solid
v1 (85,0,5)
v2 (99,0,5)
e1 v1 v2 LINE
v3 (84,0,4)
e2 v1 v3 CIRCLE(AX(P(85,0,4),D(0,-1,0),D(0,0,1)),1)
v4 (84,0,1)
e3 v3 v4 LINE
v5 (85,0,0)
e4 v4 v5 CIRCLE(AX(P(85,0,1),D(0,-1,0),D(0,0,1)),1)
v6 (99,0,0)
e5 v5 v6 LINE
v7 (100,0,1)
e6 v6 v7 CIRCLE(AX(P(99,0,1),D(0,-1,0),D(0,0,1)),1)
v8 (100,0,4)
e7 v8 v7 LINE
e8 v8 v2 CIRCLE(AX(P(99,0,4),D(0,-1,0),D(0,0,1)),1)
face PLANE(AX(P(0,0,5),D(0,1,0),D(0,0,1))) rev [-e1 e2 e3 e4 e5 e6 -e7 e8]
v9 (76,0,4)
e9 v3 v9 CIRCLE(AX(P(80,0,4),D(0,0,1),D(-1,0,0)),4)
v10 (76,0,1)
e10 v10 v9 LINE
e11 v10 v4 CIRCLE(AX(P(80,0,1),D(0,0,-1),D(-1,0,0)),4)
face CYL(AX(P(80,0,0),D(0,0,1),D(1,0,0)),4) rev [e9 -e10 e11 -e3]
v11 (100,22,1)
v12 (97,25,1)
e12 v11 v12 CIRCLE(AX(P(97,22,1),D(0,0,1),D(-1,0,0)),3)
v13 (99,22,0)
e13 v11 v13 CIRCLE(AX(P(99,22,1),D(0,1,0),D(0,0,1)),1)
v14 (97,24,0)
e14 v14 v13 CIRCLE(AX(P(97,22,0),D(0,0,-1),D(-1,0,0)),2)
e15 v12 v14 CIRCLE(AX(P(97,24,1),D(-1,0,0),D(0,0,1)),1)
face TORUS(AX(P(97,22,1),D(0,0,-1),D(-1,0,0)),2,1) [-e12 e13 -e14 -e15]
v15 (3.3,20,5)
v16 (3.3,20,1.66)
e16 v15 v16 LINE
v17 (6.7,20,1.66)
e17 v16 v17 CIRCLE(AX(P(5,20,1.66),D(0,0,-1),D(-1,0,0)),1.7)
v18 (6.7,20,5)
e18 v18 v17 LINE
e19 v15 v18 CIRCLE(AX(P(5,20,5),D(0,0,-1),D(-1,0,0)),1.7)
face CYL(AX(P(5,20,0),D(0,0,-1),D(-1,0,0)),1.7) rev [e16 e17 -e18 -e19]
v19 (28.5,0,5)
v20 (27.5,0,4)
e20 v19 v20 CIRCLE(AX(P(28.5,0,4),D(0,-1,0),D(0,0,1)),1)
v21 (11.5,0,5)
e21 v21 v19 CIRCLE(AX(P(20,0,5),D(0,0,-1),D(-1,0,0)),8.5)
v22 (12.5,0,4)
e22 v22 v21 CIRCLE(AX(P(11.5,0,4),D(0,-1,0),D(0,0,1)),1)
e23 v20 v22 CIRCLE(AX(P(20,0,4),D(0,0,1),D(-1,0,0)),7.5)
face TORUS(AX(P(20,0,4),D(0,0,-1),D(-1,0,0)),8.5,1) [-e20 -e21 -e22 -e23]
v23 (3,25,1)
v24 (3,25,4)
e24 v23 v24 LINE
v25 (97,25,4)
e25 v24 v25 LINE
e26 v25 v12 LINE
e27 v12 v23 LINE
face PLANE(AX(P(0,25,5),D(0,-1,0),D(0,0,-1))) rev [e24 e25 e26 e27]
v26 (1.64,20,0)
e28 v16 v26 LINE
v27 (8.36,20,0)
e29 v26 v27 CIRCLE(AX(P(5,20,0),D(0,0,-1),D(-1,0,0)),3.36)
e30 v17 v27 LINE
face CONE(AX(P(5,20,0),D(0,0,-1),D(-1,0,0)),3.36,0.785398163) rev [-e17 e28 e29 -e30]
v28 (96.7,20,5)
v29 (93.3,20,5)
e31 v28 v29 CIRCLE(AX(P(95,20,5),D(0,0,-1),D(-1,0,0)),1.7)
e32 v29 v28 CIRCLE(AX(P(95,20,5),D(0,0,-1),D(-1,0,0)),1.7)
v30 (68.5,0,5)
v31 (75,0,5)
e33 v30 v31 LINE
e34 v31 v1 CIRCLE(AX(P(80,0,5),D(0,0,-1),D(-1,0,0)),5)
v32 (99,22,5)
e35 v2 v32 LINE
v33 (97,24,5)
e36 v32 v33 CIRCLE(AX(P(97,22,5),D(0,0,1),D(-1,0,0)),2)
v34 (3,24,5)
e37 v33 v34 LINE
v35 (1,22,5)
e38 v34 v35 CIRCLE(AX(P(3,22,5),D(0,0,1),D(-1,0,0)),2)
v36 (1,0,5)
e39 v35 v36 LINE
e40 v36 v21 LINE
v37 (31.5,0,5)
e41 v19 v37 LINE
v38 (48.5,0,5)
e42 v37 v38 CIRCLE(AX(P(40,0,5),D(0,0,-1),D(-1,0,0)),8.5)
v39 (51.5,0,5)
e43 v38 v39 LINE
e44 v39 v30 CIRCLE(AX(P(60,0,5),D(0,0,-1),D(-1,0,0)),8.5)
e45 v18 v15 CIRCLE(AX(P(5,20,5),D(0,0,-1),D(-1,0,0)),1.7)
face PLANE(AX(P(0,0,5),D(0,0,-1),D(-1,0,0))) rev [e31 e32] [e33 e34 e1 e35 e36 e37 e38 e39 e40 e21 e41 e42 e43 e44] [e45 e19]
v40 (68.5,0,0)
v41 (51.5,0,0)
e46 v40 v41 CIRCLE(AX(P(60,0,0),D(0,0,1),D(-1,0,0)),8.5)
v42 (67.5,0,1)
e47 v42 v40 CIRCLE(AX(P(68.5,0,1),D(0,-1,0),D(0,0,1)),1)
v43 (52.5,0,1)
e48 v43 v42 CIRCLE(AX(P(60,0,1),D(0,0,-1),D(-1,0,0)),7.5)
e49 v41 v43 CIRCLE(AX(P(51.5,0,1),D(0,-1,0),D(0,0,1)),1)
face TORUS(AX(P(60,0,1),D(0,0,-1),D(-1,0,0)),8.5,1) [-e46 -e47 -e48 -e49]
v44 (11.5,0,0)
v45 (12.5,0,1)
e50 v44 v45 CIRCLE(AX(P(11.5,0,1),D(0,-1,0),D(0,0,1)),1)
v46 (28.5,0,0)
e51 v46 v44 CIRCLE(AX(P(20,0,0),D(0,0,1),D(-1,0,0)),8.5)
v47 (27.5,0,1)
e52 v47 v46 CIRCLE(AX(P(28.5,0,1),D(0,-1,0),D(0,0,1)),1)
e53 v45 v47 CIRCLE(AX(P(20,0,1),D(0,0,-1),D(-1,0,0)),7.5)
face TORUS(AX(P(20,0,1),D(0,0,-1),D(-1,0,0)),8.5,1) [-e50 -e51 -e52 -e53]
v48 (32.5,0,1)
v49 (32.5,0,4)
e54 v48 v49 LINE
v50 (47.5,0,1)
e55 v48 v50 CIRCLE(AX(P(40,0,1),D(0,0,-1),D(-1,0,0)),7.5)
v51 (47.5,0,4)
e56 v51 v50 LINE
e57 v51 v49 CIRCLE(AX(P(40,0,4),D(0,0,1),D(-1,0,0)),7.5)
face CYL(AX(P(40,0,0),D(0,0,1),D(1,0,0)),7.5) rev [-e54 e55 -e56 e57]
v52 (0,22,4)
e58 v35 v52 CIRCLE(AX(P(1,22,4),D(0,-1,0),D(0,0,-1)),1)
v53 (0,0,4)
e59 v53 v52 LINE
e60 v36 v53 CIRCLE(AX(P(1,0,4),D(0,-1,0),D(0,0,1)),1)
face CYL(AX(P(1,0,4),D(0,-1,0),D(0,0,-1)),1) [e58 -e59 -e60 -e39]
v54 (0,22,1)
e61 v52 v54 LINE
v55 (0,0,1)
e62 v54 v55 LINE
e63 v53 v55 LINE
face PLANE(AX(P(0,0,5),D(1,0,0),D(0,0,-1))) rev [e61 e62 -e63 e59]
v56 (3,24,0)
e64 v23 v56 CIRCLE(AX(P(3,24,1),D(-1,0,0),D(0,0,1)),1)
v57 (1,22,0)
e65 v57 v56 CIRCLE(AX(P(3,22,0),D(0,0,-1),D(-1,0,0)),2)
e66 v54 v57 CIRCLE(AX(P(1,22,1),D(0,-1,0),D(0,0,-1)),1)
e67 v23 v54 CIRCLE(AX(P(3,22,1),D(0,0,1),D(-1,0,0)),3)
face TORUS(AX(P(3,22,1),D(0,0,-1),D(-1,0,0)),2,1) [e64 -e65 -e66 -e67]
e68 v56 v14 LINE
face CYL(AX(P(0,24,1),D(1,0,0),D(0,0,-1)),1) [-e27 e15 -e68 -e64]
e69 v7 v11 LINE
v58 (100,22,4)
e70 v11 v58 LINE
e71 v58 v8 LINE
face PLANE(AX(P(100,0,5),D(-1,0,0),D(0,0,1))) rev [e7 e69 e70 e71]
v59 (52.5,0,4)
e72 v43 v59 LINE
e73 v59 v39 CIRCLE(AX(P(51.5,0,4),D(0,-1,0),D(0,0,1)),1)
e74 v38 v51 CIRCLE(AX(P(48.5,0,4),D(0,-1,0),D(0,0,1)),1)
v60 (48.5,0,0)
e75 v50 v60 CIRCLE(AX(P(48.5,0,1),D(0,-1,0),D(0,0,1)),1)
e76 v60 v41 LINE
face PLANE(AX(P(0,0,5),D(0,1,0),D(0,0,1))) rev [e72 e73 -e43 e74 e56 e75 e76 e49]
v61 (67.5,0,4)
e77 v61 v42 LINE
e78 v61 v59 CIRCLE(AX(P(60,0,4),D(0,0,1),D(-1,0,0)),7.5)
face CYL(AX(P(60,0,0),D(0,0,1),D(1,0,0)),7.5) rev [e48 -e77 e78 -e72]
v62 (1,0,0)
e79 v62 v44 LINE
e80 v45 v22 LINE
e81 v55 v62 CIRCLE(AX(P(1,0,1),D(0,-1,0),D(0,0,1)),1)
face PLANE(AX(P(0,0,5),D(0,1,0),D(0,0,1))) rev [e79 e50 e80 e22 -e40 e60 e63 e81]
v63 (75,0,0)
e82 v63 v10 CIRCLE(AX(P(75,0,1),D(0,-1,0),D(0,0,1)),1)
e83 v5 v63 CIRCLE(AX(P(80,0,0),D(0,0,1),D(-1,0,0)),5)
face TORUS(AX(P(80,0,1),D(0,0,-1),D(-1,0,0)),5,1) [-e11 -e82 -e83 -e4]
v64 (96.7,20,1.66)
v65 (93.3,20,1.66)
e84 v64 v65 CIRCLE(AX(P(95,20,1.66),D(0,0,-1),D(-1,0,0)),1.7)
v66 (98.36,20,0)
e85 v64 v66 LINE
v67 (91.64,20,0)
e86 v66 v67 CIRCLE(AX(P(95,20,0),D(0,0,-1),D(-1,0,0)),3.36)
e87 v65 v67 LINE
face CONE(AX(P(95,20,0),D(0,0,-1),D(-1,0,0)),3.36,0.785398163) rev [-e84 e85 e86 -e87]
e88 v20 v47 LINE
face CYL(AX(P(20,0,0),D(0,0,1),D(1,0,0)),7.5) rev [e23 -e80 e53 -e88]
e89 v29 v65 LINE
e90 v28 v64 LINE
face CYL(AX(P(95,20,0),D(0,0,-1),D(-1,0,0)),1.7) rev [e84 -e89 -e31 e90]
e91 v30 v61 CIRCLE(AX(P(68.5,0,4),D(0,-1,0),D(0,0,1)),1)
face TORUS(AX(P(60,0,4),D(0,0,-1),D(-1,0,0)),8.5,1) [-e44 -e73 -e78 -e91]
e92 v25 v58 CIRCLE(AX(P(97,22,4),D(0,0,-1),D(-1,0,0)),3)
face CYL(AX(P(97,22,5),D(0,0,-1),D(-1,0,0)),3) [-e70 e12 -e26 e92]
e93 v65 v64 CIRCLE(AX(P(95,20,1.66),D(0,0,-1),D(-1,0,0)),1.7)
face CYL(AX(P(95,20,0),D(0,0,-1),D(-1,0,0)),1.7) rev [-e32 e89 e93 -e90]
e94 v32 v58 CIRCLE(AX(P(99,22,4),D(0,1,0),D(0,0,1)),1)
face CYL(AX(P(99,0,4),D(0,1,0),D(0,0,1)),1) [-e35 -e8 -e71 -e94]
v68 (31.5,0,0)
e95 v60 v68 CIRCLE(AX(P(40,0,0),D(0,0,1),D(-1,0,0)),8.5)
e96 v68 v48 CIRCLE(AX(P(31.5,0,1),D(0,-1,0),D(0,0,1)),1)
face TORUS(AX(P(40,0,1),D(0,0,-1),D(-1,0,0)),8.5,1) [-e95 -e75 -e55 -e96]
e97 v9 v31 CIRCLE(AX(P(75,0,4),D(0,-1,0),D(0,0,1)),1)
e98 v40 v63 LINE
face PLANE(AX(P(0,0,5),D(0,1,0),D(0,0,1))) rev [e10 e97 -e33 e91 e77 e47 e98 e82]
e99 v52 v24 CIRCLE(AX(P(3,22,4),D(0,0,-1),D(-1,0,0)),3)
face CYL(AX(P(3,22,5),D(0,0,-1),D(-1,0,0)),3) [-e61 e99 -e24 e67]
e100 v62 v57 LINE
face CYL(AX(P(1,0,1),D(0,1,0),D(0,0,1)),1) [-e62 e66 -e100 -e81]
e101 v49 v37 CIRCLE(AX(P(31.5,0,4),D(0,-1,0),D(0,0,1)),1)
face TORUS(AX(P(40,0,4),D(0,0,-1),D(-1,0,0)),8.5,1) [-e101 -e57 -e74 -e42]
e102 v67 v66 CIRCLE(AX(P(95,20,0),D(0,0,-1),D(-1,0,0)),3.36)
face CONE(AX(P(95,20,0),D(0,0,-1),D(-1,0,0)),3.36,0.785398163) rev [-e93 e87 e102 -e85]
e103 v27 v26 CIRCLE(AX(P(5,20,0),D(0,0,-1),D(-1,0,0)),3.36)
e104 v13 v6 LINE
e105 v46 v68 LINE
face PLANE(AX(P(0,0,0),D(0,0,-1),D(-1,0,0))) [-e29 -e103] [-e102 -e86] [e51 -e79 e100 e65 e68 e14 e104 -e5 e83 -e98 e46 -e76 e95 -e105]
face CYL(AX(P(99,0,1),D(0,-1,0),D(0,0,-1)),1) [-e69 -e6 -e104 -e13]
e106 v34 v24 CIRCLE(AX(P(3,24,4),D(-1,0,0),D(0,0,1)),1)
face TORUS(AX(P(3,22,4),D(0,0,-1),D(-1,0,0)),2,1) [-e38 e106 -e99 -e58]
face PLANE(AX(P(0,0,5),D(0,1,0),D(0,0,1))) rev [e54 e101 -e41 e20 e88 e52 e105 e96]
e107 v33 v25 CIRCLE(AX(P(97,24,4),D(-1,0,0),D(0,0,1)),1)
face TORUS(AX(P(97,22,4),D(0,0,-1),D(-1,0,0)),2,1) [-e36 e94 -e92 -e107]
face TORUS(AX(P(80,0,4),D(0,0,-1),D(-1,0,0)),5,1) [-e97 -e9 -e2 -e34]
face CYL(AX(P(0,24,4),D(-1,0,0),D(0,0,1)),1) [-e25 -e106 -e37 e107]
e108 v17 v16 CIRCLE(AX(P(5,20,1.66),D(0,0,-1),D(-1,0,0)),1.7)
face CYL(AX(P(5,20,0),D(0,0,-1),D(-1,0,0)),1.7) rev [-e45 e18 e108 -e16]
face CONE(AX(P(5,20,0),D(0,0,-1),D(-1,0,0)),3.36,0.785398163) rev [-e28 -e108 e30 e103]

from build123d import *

# Parameters (mm, degrees)
SKETCH_1_W                   = 100
SKETCH_1_H                   = 25
EXTRUDE_1_DEPTH              = 5
SKETCH_2_R                   = 7.5
SKETCH_2_R_2                 = 4
CUT_EXTRUDE_1_DEPTH          = 104.198837203
HOLE_WIZARD_M3_1_D           = 3.4
HOLE_WIZARD_M3_1_CSINK_D     = 6.72
HOLE_WIZARD_M3_1_CSINK_ANGLE = 90
FILLET_1_R                   = 3
FILLET_2_R                   = 1


with BuildPart() as part:
    # 草图1 → 凸台-拉伸1 (new body)
    with BuildSketch(Plane.XY):
        with Locations((50, 12.5)):
            Rectangle(SKETCH_1_W, SKETCH_1_H)
    extrude(amount=EXTRUDE_1_DEPTH)

    # 草图2 → 切除-拉伸1 (cut, through all)
    with BuildSketch(Plane.XY.offset(5)):
        with Locations((20, 0)):
            Circle(SKETCH_2_R)
        with Locations((40, 0)):
            Circle(SKETCH_2_R)
        with Locations((60, 0)):
            Circle(SKETCH_2_R)
        with Locations((80, 0)):
            Circle(SKETCH_2_R_2)
    extrude(amount=-CUT_EXTRUDE_1_DEPTH, mode=Mode.SUBTRACT)

    # M3 六角凹锥坑螺钉的锥形沉头孔1 (through all)
    with Locations(Plane(origin=(0, 0, 0), x_dir=(-1, 0, 0), z_dir=(0, 0, -1))):
        with Locations((-5, 20), (-95, 20)):
            CounterSinkHole(HOLE_WIZARD_M3_1_D / 2, HOLE_WIZARD_M3_1_CSINK_D / 2, counter_sink_angle=HOLE_WIZARD_M3_1_CSINK_ANGLE)

    # 圆角1
    fillet_1_edges = [part.edges().sort_by_distance(p)[0] for p in [
        (0, 25, 2.5),
        (100, 25, 2.5),
    ]]
    fillet(fillet_1_edges, radius=FILLET_1_R)

    # 圆角2
    fillet_2_edges = [part.edges().sort_by_distance(p)[0] for p in [
        (100, 11, 5),
        (20, 7.5, 5),
        (20, 7.5, 0),
        (40, 7.5, 5),
        (40, 7.5, 0),
        (60, 7.5, 5),
        (60, 7.5, 0),
        (80, 4, 5),
        (80, 4, 0),
        (100, 11, 0),
        (50, 25, 0),
        (50, 25, 5),
        (0, 11, 0),
        (0.878679656, 24.121320344, 0),
        (99.121320344, 24.121320344, 0),
        (0, 11, 5),
        (0.878679656, 24.121320344, 5),
        (99.121320344, 24.121320344, 5),
    ]]
    fillet(fillet_2_edges, radius=FILLET_2_R)


solid = part.part
